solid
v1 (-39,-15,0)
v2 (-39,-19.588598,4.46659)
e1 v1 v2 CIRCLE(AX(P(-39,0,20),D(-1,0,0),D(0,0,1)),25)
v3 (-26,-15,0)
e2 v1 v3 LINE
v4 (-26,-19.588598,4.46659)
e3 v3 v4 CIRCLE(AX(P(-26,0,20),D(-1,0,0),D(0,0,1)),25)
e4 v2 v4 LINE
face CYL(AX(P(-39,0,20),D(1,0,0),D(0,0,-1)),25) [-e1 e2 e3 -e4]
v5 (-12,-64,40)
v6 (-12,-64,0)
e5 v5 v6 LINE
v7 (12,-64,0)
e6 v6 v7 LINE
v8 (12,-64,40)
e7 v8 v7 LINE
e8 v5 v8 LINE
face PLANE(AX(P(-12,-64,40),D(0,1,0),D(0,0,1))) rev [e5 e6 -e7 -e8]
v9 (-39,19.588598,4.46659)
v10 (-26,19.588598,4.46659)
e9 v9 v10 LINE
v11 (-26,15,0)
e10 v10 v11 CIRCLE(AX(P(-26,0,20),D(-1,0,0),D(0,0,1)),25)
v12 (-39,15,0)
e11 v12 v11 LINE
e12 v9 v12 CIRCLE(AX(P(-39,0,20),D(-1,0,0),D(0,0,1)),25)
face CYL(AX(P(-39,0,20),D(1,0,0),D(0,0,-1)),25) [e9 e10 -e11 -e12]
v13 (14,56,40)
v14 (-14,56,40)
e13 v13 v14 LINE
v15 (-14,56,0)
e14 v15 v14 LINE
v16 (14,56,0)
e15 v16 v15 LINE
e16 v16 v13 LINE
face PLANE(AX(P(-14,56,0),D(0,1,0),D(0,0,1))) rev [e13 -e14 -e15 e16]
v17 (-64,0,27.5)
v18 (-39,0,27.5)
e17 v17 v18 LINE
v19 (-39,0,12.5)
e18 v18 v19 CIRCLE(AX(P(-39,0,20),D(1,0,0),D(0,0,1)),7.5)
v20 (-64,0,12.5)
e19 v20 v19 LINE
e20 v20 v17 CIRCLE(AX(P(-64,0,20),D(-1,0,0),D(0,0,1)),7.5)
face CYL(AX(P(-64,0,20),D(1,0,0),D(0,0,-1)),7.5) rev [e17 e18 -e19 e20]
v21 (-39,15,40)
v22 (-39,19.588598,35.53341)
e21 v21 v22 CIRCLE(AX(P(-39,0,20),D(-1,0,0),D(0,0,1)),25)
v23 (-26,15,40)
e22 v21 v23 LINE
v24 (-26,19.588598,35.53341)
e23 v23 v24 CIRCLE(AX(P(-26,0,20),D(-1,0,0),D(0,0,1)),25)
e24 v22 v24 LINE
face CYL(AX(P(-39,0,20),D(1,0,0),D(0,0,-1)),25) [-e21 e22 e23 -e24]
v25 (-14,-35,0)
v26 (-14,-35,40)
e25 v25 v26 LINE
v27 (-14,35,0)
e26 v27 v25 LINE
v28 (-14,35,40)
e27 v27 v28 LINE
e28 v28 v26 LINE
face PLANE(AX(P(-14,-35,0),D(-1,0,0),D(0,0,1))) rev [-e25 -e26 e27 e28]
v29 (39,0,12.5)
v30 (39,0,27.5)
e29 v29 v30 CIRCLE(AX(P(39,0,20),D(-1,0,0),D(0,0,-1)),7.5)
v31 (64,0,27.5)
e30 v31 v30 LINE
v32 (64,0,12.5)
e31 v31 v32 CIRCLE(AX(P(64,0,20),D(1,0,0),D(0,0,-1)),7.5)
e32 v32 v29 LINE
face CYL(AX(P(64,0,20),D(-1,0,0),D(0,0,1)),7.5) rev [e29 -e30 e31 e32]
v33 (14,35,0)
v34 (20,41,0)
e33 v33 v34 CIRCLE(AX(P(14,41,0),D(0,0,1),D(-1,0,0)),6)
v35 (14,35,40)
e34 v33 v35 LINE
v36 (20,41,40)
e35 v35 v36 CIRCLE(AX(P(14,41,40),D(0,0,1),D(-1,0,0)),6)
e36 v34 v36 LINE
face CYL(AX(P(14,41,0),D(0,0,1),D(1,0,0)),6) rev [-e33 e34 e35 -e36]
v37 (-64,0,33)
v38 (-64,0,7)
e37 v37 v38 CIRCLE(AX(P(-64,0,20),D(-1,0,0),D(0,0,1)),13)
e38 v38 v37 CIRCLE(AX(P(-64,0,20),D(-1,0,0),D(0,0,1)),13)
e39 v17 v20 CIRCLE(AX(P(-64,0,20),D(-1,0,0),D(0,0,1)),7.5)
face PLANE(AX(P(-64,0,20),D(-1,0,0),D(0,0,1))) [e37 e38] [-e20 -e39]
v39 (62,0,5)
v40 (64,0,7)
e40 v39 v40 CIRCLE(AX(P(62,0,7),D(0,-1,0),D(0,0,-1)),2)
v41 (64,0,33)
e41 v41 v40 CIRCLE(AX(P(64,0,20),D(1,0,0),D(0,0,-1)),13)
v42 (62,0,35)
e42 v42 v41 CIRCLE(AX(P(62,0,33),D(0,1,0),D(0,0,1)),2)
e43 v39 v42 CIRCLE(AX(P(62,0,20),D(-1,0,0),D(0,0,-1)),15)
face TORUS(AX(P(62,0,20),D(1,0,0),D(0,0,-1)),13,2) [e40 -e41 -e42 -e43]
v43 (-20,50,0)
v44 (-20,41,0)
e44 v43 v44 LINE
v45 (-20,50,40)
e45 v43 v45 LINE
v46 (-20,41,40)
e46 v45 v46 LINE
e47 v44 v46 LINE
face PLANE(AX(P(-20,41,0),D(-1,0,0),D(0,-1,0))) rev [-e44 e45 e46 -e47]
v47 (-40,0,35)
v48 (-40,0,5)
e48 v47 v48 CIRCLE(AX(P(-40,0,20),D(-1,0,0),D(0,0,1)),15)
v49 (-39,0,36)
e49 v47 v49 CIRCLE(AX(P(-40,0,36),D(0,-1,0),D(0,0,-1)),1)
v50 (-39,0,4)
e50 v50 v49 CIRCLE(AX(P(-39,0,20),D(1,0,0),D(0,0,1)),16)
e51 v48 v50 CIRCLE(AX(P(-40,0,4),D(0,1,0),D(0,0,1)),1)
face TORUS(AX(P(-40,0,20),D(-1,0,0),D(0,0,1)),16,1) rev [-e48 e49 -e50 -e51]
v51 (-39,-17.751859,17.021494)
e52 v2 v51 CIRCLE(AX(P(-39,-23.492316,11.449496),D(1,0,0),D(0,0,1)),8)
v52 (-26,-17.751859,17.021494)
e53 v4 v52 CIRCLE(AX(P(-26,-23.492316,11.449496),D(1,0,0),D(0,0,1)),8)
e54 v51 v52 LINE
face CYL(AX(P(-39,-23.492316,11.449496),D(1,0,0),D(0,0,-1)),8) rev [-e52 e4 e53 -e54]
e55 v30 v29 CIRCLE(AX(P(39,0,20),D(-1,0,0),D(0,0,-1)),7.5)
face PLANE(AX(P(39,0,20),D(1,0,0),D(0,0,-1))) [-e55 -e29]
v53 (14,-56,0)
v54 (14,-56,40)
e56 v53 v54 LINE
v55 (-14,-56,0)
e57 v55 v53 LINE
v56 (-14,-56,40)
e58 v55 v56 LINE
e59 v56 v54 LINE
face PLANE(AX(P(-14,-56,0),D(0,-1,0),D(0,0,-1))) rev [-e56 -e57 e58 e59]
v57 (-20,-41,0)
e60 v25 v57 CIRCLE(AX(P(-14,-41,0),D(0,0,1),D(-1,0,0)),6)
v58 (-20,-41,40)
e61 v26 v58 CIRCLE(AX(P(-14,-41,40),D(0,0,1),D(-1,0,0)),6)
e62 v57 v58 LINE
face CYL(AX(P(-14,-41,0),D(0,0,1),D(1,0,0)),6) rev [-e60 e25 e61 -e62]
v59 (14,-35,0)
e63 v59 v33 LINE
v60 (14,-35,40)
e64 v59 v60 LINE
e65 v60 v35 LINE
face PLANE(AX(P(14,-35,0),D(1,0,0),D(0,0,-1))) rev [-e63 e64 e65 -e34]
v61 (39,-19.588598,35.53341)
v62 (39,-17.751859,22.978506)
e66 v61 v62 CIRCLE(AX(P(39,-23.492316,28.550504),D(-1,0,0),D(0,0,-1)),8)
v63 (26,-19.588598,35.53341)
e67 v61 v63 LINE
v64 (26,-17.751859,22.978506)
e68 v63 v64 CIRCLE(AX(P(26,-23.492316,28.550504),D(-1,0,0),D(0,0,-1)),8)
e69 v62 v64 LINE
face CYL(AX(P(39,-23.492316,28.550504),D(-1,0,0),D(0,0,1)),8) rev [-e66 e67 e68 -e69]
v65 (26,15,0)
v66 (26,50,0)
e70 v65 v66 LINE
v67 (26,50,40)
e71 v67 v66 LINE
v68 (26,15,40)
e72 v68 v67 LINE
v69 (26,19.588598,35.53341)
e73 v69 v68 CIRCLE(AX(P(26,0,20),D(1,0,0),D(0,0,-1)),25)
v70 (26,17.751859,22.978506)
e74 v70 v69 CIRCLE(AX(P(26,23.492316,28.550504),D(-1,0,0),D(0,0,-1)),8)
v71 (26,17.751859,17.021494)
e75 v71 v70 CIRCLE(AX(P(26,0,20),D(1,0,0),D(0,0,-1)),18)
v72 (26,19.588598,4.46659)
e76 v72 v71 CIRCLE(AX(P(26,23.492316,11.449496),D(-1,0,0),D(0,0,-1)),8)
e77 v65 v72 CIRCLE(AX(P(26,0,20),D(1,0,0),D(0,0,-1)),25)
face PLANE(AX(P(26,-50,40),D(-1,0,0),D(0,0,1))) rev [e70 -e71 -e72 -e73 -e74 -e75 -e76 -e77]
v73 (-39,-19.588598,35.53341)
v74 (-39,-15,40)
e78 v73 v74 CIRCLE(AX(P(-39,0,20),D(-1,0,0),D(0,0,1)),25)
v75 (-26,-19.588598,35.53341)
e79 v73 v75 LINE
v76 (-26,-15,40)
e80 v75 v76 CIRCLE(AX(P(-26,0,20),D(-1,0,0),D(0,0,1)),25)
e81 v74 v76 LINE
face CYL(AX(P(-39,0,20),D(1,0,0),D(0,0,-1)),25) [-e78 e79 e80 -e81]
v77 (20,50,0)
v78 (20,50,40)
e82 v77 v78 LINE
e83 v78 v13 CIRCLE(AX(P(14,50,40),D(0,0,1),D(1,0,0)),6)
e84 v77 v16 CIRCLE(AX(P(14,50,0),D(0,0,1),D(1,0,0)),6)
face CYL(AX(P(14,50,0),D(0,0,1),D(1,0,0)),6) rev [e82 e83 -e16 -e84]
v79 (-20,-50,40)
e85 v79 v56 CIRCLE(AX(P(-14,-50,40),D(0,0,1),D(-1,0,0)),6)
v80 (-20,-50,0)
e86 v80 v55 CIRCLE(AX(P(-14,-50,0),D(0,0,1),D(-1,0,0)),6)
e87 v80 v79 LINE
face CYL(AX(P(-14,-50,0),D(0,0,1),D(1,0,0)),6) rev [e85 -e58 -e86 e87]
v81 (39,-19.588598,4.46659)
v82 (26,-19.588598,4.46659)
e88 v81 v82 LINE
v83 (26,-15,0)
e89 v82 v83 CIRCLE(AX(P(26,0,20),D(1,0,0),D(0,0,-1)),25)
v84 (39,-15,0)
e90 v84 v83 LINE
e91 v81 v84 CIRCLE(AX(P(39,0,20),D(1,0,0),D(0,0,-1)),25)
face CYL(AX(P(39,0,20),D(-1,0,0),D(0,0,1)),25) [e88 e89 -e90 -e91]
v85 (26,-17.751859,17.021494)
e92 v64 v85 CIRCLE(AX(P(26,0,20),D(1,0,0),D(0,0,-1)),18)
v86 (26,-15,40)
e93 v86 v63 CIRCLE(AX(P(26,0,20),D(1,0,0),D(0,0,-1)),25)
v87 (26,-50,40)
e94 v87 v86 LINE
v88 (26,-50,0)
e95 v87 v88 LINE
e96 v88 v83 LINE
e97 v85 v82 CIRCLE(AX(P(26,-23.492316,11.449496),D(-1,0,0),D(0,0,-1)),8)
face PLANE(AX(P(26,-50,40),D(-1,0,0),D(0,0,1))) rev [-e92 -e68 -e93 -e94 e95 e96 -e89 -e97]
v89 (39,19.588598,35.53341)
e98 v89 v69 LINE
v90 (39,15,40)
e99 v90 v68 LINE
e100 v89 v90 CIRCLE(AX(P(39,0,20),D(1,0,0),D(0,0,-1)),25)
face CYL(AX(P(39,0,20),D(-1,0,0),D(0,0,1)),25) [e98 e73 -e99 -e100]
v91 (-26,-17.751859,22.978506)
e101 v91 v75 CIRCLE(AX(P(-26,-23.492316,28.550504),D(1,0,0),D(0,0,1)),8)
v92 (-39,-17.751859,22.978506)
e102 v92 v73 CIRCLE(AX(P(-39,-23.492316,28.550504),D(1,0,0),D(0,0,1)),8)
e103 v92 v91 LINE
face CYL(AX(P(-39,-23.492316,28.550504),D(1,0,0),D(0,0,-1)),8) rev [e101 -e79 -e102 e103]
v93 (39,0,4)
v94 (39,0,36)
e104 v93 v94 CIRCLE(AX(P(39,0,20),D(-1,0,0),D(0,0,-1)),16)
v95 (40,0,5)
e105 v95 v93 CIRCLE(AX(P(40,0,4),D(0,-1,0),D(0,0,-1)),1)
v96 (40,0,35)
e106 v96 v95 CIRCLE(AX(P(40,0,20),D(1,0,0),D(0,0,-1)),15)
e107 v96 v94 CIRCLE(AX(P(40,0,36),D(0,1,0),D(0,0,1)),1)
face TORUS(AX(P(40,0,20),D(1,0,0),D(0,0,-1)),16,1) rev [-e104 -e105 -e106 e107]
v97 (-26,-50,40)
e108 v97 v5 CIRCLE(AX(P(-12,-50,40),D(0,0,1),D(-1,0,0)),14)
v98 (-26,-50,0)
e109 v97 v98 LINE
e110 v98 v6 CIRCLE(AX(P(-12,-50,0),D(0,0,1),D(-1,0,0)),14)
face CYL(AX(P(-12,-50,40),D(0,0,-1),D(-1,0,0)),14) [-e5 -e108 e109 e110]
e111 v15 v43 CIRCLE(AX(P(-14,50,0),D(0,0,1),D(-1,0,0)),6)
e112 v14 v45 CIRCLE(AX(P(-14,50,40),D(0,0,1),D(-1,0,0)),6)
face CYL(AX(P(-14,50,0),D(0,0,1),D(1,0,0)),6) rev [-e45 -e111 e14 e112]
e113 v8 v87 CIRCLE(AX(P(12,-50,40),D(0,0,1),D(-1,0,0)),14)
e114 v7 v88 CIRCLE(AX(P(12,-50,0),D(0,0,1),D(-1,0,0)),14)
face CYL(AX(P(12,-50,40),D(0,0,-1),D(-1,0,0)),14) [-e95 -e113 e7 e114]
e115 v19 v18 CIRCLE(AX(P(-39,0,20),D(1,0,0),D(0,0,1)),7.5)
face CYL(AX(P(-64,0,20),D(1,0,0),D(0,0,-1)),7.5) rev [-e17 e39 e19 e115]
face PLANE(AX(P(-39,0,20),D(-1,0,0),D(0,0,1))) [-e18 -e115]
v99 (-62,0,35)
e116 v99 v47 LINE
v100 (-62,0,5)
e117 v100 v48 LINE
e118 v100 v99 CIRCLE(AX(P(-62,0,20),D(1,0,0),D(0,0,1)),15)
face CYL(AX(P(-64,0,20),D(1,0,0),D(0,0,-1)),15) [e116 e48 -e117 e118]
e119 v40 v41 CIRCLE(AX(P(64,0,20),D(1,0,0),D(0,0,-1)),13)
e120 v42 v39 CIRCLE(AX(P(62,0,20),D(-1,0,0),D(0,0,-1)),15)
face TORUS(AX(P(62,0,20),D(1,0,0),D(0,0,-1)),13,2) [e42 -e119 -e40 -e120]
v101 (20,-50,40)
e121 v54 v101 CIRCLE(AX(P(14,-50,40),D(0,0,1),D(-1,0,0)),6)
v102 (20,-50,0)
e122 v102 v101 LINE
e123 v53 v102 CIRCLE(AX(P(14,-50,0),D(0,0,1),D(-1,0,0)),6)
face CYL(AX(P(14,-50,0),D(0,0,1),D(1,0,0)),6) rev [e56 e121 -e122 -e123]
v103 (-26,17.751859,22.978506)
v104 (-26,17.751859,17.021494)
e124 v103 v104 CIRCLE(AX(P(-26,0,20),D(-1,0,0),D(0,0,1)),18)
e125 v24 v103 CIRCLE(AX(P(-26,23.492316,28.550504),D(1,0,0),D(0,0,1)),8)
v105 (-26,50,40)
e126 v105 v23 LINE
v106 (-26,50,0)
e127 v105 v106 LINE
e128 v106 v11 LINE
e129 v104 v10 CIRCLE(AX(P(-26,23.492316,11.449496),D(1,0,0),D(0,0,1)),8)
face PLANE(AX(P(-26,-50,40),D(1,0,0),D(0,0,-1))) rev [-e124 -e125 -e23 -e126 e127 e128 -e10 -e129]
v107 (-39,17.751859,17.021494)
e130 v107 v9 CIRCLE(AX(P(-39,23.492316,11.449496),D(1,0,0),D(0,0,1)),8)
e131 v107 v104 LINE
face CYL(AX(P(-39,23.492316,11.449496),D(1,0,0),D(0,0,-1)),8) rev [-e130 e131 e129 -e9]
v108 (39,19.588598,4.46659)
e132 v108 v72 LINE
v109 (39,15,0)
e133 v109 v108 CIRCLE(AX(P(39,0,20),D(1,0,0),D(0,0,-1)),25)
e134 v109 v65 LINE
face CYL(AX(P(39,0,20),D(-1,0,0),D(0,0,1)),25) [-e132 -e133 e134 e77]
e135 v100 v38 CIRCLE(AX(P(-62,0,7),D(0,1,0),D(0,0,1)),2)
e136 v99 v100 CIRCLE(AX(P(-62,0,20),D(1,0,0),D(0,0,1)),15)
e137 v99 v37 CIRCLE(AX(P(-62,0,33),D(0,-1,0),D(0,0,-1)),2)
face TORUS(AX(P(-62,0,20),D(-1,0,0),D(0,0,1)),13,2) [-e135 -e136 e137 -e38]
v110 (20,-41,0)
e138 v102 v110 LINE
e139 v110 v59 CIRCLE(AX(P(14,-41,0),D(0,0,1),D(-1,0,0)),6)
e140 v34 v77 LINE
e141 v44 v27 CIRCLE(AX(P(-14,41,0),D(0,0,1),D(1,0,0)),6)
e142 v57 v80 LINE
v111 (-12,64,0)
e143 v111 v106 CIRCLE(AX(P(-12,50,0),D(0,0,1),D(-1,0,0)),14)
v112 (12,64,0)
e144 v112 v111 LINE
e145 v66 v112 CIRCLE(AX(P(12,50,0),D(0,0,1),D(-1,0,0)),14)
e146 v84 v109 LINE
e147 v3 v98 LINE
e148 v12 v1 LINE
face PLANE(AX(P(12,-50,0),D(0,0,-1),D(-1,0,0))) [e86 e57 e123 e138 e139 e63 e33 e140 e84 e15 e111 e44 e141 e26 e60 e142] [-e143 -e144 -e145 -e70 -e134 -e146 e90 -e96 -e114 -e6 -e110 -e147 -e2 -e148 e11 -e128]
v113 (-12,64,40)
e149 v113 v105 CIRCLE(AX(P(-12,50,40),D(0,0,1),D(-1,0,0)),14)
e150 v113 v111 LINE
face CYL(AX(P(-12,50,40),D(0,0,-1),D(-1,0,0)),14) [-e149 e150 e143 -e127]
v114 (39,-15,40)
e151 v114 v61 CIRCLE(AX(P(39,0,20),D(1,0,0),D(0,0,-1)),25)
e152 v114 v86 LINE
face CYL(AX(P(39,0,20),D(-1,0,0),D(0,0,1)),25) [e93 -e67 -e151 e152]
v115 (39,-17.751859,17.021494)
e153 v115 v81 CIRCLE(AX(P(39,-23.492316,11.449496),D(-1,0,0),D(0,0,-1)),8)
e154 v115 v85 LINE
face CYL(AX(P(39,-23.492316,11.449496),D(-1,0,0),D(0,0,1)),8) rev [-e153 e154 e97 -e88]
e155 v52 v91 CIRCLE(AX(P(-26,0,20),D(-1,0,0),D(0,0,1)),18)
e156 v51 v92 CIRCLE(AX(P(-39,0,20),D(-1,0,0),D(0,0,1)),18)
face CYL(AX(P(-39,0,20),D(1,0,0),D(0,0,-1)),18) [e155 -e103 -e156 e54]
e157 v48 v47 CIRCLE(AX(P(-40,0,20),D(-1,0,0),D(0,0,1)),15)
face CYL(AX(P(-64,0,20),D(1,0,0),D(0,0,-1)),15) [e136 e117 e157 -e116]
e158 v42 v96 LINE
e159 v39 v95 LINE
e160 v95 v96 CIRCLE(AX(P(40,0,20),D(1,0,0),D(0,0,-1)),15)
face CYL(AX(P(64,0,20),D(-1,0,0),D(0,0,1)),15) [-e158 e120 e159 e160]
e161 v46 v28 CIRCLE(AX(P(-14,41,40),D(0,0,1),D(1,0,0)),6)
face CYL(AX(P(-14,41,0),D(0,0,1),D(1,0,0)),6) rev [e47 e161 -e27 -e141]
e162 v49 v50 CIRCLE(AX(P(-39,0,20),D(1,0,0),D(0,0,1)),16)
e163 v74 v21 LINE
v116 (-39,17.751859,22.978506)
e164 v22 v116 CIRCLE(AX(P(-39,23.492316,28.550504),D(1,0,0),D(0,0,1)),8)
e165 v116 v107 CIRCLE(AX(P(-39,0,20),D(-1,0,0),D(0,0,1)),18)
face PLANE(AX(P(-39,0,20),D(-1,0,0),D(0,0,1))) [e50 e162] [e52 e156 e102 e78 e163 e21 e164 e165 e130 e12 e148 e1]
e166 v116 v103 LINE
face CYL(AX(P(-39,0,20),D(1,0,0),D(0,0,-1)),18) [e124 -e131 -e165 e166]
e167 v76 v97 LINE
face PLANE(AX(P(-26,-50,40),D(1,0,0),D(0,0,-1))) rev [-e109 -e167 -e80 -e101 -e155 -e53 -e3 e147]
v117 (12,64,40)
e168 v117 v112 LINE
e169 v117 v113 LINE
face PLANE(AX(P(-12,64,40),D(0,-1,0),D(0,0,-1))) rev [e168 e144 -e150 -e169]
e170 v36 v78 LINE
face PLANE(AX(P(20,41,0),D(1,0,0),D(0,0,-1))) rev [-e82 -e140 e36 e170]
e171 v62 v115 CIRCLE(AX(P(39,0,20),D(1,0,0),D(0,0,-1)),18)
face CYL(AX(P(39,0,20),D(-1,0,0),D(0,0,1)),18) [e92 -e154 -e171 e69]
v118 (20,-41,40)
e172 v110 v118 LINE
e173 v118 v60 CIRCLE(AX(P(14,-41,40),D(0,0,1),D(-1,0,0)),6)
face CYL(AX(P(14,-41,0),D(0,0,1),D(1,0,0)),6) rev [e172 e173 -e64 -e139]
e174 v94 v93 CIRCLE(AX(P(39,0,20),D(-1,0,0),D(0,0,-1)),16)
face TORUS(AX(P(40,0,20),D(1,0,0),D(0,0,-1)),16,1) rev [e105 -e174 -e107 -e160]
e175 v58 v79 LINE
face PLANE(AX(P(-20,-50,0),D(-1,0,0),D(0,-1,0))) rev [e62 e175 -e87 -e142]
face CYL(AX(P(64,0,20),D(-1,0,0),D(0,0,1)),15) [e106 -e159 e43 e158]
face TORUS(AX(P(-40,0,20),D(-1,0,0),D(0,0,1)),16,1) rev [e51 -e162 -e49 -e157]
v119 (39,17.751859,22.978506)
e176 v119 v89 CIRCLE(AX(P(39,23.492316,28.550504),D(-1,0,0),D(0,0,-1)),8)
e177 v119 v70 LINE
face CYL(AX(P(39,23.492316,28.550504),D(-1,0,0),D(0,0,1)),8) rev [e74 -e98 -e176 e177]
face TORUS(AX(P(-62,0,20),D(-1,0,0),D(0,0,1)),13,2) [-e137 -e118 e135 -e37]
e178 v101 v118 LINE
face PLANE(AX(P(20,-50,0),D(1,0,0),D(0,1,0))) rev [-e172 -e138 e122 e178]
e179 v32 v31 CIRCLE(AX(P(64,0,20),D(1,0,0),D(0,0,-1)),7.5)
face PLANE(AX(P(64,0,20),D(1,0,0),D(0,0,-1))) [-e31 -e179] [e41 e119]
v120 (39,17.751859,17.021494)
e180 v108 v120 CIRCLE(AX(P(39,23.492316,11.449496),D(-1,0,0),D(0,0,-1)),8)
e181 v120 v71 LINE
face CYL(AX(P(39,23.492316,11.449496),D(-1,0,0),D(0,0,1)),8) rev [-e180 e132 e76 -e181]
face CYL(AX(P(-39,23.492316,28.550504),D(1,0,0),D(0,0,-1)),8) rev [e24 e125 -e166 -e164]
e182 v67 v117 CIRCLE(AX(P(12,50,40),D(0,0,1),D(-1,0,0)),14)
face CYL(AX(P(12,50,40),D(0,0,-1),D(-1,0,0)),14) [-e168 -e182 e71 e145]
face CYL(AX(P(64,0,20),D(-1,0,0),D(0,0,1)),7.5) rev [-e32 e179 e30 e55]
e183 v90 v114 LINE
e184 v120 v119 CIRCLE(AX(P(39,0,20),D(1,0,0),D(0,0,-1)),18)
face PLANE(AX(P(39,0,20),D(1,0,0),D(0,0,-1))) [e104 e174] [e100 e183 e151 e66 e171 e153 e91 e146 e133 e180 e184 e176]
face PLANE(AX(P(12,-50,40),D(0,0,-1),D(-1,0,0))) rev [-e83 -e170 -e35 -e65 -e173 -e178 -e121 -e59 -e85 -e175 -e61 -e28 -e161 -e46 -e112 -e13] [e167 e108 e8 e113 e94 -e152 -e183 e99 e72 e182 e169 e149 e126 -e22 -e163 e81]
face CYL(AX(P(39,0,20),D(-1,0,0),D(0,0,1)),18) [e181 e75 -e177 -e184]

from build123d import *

# Parameters (mm, degrees)
FRAME_BODY_DEPTH         = 40
FRAME_WINDOW_CUT_DEPTH   = 40
SIDE_LUG_A_DEPTH         = 13
SPIGOT_A_SKETCH_R        = 15
SPIGOT_A_SKETCH_R_2      = 7.5
SPIGOT_A_30_DEPTH        = 25
SIDE_START               = 13
SIDE_LUG_B_DEPTH         = 13
SPIGOT_START             = 25
SPIGOT_B_SKETCH_R        = 15
SPIGOT_B_SKETCH_R_2      = 7.5
SPIGOT_B_30_DEPTH        = 25
SPIGOT_EDGE_FILLETS_R2_R = 2
LUG_BLEND_FILLETS_R1_R   = 1


with BuildPart() as part:
    # Frame Profile Sketch → Frame Body (new body)
    with BuildSketch(Plane.XY):
        with BuildLine():
            Line((-12, -64), (12, -64))
            ThreePointArc((12, -64), (21.899494937, -59.899494937), (26, -50))
            Line((26, -50), (26, 50))
            ThreePointArc((26, 50), (21.899494937, 59.899494937), (12, 64))
            Line((12, 64), (-12, 64))
            ThreePointArc((-12, 64), (-21.899494937, 59.899494937), (-26, 50))
            Line((-26, 50), (-26, -50))
            ThreePointArc((-26, -50), (-21.899494937, -59.899494937), (-12, -64))
        make_face()
    extrude(amount=FRAME_BODY_DEPTH)

    # Frame Window Sketch → Frame Window Cut (cut)
    with BuildSketch(Plane.XY.offset(40)):
        with BuildLine():
            Line((14, -35), (14, 35))
            ThreePointArc((14, 35), (18.242640687, 36.757359313), (20, 41))
            Line((20, 41), (20, 50))
            ThreePointArc((20, 50), (18.242640687, 54.242640687), (14, 56))
            Line((14, 56), (-14, 56))
            ThreePointArc((-14, 56), (-18.242640687, 54.242640687), (-20, 50))
            Line((-20, 50), (-20, 41))
            ThreePointArc((-20, 41), (-18.242640687, 36.757359313), (-14, 35))
            Line((-14, 35), (-14, -35))
            ThreePointArc((-14, -35), (-18.242640687, -36.757359313), (-20, -41))
            Line((-20, -41), (-20, -50))
            ThreePointArc((-20, -50), (-18.242640687, -54.242640687), (-14, -56))
            Line((-14, -56), (14, -56))
            ThreePointArc((14, -56), (18.242640687, -54.242640687), (20, -50))
            Line((20, -50), (20, -41))
            ThreePointArc((20, -41), (18.242640687, -36.757359313), (14, -35))
        make_face()
    extrude(amount=-FRAME_WINDOW_CUT_DEPTH, mode=Mode.SUBTRACT)

    # Side Lug A Sketch → Side Lug A (add)
    with BuildSketch(Plane(origin=(26, 0, 0), x_dir=(0, 0, -1), z_dir=(1, 0, 0))):
        with BuildLine():
            Line((-40, 15), (-40, -15))
            ThreePointArc((-40, -15), (-37.914229564, -17.437900652), (-35.533410394, -19.588597743))
            ThreePointArc((-35.533410394, -19.588597743), (-29.708548536, -15.576576016), (-22.978505654, -17.751859172))
            ThreePointArc((-22.978505654, -17.751859172), (-20, -18), (-17.021494346, -17.751859172))
            ThreePointArc((-17.021494346, -17.751859172), (-10.291451464, -15.576576016), (-4.466589606, -19.588597743))
            ThreePointArc((-4.466589606, -19.588597743), (-2.085770436, -17.437900652), (0, -15))
            Line((0, -15), (0, 15))
            ThreePointArc((0, 15), (-2.085770436, 17.437900652), (-4.466589606, 19.588597743))
            ThreePointArc((-4.466589606, 19.588597743), (-10.291451464, 15.576576016), (-17.021494346, 17.751859172))
            ThreePointArc((-17.021494346, 17.751859172), (-20, 18), (-22.978505654, 17.751859172))
            ThreePointArc((-22.978505654, 17.751859172), (-29.708548536, 15.576576016), (-35.533410394, 19.588597743))
            ThreePointArc((-35.533410394, 19.588597743), (-37.914229564, 17.437900652), (-40, 15))
        make_face()
    extrude(amount=SIDE_LUG_A_DEPTH)

    # Spigot A Sketch → Spigot A Ø30 (add)
    with BuildSketch(Plane(origin=(39, 0, 0), x_dir=(0, 0, -1), z_dir=(1, 0, 0))):
        with Locations((-20, 0)):
            Circle(SPIGOT_A_SKETCH_R)
        with Locations((-20, 0)):
            Circle(SPIGOT_A_SKETCH_R_2, mode=Mode.SUBTRACT)
    extrude(amount=SPIGOT_A_30_DEPTH)

    # Side Lug B Sketch → Side Lug B (add)
    with BuildSketch(Plane.ZY.offset(26).offset(SIDE_START)):
        with BuildLine():
            Line((0, 15), (0, -15))
            ThreePointArc((0, -15), (2.085770436, -17.437900652), (4.466589606, -19.588597743))
            ThreePointArc((4.466589606, -19.588597743), (10.291451464, -15.576576016), (17.021494346, -17.751859172))
            ThreePointArc((17.021494346, -17.751859172), (20, -18), (22.978505654, -17.751859172))
            ThreePointArc((22.978505654, -17.751859172), (29.708548536, -15.576576016), (35.533410394, -19.588597743))
            ThreePointArc((35.533410394, -19.588597743), (37.914229564, -17.437900652), (40, -15))
            Line((40, -15), (40, 15))
            ThreePointArc((40, 15), (37.914229564, 17.437900652), (35.533410394, 19.588597743))
            ThreePointArc((35.533410394, 19.588597743), (29.708548536, 15.576576016), (22.978505654, 17.751859172))
            ThreePointArc((22.978505654, 17.751859172), (20, 18), (17.021494346, 17.751859172))
            ThreePointArc((17.021494346, 17.751859172), (10.291451464, 15.576576016), (4.466589606, 19.588597743))
            ThreePointArc((4.466589606, 19.588597743), (2.085770436, 17.437900652), (0, 15))
        make_face()
    extrude(amount=-SIDE_LUG_B_DEPTH)

    # Spigot B Sketch → Spigot B Ø30 (add)
    with BuildSketch(Plane.ZY.offset(39).offset(SPIGOT_START)):
        with Locations(Location((20, 0, 0), (0, 0, 180))):
            Circle(SPIGOT_B_SKETCH_R)
        with Locations(Location((20, 0, 0), (0, 0, 180))):
            Circle(SPIGOT_B_SKETCH_R_2, mode=Mode.SUBTRACT)
    extrude(amount=-SPIGOT_B_30_DEPTH)

    # Spigot Edge Fillets R2
    spigot_edge_fillets_r2_edges = [part.edges().sort_by_distance(p)[0] for p in [
        (64, 0, 35),
        (-64, 0, 35),
    ]]
    fillet(spigot_edge_fillets_r2_edges, radius=SPIGOT_EDGE_FILLETS_R2_R)

    # Lug Blend Fillets R1
    lug_blend_fillets_r1_edges = [part.edges().sort_by_distance(p)[0] for p in [
        (39, 0, 35),
        (-39, 0, 35),
    ]]
    fillet(lug_blend_fillets_r1_edges, radius=LUG_BLEND_FILLETS_R1_R)


solid = part.part
